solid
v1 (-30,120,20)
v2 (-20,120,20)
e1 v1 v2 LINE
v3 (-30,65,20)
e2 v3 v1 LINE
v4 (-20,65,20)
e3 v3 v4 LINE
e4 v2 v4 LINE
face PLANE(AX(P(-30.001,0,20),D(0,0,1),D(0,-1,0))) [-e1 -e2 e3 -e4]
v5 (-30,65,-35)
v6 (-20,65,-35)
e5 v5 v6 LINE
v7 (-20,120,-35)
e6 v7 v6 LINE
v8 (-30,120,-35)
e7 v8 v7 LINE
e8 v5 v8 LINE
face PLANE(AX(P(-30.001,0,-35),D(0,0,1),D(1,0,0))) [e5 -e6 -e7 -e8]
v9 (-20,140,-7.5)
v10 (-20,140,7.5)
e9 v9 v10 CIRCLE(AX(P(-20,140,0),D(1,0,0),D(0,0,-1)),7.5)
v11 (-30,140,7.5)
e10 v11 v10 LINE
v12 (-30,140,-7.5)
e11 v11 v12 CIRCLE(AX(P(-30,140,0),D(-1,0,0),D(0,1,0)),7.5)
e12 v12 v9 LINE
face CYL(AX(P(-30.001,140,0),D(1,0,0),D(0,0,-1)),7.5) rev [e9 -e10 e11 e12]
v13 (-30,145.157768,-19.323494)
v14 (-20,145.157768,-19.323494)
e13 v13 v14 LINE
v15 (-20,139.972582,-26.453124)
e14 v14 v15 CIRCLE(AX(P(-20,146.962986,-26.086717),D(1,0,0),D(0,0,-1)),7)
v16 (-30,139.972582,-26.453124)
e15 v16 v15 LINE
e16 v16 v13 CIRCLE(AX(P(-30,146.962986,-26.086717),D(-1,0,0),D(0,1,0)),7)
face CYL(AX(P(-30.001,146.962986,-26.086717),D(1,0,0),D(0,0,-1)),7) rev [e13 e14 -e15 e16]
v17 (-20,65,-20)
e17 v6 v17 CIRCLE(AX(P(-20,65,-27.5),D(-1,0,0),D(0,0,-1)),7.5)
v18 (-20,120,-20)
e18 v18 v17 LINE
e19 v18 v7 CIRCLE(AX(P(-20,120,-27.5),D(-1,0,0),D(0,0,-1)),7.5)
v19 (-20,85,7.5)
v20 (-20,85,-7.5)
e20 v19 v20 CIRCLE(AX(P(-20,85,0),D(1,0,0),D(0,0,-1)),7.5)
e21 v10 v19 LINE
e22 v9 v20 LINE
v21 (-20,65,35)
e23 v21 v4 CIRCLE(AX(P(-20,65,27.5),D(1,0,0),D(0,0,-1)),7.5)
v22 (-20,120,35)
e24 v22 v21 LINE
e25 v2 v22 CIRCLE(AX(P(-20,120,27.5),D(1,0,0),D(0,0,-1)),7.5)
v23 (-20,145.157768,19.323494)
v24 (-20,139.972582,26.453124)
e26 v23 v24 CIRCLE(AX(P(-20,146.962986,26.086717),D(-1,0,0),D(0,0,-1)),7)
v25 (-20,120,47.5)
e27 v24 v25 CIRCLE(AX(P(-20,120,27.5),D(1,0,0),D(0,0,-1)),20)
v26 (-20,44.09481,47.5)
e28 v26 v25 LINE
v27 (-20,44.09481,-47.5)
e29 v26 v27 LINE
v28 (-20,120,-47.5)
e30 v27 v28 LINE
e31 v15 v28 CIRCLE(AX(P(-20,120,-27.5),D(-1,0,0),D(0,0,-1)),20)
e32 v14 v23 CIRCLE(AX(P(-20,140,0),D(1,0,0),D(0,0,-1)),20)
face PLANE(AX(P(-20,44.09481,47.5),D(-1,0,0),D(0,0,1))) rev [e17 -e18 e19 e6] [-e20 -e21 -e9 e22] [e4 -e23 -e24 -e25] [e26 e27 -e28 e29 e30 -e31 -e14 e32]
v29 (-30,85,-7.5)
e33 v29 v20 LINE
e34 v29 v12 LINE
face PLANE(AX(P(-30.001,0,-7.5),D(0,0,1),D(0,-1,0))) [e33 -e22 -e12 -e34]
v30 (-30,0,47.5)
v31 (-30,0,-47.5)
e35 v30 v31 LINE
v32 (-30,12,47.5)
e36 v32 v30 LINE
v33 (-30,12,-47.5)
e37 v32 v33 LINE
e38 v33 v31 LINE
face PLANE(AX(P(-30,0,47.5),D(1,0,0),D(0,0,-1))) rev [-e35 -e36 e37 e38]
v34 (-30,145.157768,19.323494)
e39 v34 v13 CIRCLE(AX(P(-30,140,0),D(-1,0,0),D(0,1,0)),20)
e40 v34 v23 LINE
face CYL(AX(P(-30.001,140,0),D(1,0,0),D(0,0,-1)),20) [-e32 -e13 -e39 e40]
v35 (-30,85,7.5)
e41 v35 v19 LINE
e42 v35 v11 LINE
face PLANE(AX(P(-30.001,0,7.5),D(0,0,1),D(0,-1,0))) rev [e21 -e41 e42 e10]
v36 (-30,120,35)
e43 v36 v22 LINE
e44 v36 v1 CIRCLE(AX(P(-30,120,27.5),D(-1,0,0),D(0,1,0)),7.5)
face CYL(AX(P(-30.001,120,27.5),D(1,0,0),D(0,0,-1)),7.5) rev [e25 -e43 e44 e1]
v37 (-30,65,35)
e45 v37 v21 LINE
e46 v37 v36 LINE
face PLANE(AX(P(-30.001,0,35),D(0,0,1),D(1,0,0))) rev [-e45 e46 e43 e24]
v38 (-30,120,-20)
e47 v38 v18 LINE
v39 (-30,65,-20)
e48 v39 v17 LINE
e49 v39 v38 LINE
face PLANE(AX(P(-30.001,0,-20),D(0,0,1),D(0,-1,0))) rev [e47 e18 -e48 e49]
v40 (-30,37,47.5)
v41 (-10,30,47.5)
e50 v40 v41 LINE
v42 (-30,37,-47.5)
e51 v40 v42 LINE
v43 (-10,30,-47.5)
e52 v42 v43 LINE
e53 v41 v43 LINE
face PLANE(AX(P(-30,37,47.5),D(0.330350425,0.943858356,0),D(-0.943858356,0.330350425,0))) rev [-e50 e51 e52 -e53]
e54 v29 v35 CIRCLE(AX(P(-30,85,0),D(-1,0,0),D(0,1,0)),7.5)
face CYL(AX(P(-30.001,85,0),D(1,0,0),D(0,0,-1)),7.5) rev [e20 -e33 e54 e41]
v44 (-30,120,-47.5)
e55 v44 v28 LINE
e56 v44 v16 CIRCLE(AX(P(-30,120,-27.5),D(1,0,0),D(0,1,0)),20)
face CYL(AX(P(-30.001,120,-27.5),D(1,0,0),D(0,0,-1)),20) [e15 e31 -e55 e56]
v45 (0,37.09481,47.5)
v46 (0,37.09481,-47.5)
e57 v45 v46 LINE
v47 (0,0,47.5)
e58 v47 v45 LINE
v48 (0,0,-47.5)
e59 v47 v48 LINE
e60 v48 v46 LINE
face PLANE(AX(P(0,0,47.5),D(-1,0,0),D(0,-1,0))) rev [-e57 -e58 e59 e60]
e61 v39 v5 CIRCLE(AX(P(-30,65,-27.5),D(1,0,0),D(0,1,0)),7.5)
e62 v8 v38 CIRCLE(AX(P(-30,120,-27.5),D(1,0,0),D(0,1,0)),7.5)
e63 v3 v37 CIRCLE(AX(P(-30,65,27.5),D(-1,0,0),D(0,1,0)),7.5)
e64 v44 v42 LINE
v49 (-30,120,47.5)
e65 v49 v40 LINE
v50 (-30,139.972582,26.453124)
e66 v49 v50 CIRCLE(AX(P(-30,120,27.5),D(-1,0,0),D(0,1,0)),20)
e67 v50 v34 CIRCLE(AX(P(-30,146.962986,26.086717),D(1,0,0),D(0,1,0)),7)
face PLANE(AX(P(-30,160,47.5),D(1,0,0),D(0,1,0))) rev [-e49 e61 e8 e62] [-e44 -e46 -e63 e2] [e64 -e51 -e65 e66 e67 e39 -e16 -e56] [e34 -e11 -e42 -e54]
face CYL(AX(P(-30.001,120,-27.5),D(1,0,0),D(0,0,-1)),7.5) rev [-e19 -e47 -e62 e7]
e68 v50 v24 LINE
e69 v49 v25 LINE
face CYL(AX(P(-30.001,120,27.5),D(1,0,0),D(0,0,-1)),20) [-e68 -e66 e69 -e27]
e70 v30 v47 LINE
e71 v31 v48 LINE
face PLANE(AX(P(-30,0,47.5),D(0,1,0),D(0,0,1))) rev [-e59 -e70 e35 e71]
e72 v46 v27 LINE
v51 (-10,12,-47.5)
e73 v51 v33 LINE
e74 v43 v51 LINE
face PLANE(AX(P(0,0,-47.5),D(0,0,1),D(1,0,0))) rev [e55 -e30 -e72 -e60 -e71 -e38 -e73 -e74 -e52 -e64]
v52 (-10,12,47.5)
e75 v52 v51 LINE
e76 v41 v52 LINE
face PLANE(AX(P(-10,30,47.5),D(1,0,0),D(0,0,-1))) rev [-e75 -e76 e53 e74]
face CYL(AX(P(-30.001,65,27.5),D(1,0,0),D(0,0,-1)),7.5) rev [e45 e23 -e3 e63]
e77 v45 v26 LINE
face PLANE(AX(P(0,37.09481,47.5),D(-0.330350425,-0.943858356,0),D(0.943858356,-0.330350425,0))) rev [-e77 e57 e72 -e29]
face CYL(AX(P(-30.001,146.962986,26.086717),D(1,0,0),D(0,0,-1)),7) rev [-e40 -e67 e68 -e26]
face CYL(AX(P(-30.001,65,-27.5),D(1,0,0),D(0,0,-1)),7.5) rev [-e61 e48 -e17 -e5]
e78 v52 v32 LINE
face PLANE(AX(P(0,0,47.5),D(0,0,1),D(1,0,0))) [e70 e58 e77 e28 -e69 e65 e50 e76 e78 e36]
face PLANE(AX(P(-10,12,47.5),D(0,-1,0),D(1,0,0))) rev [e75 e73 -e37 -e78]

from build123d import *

# Parameters (mm, degrees)
SUPPORT_BODY_DEPTH         = 47.5
MOUNTING_SLOTS_3X7MM_REACH = 170.096


with BuildPart() as part:
    # Support Profile Sketch → Support Body (new, symmetric)
    with BuildSketch(Plane.XY):
        Polygon((-30, 0), (0, 0), (0, 37.09481005), (-20, 44.09481005), (-20, 160), (-30, 160), (-30, 37), (-10, 30), (-10, 12), (-30, 12), align=None)
    extrude(amount=SUPPORT_BODY_DEPTH, both=True)

    # Mounting Slots Sketch → Mounting Slots 3x7mm (cut, up to next)
    with BuildSketch(Plane(origin=(-20, 0, 0), x_dir=(0, 0, -1), z_dir=(1, 0, 0)), mode=Mode.PRIVATE) as mounting_slots_3x7mm_sk1:
        with BuildLine():
            Line((-35, 120), (-35, 65))
            ThreePointArc((-35, 65), (-27.5, 57.5), (-20, 65))
            Line((-20, 65), (-20, 120))
            ThreePointArc((-20, 120), (-27.5, 127.5), (-35, 120))
        make_face()
    mounting_slots_3x7mm_tool1 = extrude(mounting_slots_3x7mm_sk1.sketch, amount=-MOUNTING_SLOTS_3X7MM_REACH, mode=Mode.PRIVATE) & part.part
    # Mounting Slots Sketch → Mounting Slots 3x7mm (cut, up to next)
    with BuildSketch(Plane(origin=(-20, 0, 0), x_dir=(0, 0, -1), z_dir=(1, 0, 0)), mode=Mode.PRIVATE) as mounting_slots_3x7mm_sk2:
        with BuildLine():
            Line((-7.5, 140), (-7.5, 85))
            ThreePointArc((-7.5, 85), (0, 77.5), (7.5, 85))
            Line((7.5, 85), (7.5, 140))
            ThreePointArc((7.5, 140), (0, 147.5), (-7.5, 140))
        make_face()
    mounting_slots_3x7mm_tool2 = extrude(mounting_slots_3x7mm_sk2.sketch, amount=-MOUNTING_SLOTS_3X7MM_REACH, mode=Mode.PRIVATE) & part.part
    # Mounting Slots Sketch → Mounting Slots 3x7mm (cut, up to next)
    with BuildSketch(Plane(origin=(-20, 0, 0), x_dir=(0, 0, -1), z_dir=(1, 0, 0)), mode=Mode.PRIVATE) as mounting_slots_3x7mm_sk3:
        with BuildLine():
            ThreePointArc((35, 65), (27.5, 57.5), (20, 65))
            Line((20, 65), (20, 120))
            ThreePointArc((20, 120), (27.5, 127.5), (35, 120))
            Line((35, 120), (35, 65))
        make_face()
    mounting_slots_3x7mm_tool3 = extrude(mounting_slots_3x7mm_sk3.sketch, amount=-MOUNTING_SLOTS_3X7MM_REACH, mode=Mode.PRIVATE) & part.part
    # Mounting Slots Sketch → Mounting Slots 3x7mm (cut, up to next)
    with BuildSketch(Plane(origin=(-20, 0, 0), x_dir=(0, 0, -1), z_dir=(1, 0, 0)), mode=Mode.PRIVATE) as mounting_slots_3x7mm_sk4:
        with BuildLine():
            ThreePointArc((26.453123952, 139.97258247), (41.267034521, 134.507541504), (47.5, 120))
            Line((47.5, 120), (47.5, 160))
            Line((47.5, 160), (1.13e-07, 160))
            ThreePointArc((1.13e-07, 160), (12.182870127, 155.861200316), (19.323494322, 145.157767656))
            ThreePointArc((19.323494322, 145.157767656), (21.969515451, 141.301833745), (26.453123952, 139.97258247))
        make_face()
    mounting_slots_3x7mm_tool4 = extrude(mounting_slots_3x7mm_sk4.sketch, amount=-MOUNTING_SLOTS_3X7MM_REACH, mode=Mode.PRIVATE) & part.part
    # Mounting Slots Sketch → Mounting Slots 3x7mm (cut, up to next)
    with BuildSketch(Plane(origin=(-20, 0, 0), x_dir=(0, 0, -1), z_dir=(1, 0, 0)), mode=Mode.PRIVATE) as mounting_slots_3x7mm_sk5:
        with BuildLine():
            ThreePointArc((-19.323494322, 145.157767656), (-12.182870037, 155.861200385), (1.13e-07, 160))
            Line((1.13e-07, 160), (-47.5, 160))
            Line((-47.5, 160), (-47.5, 120))
            ThreePointArc((-47.5, 120), (-41.267034521, 134.507541504), (-26.453123952, 139.97258247))
            ThreePointArc((-26.453123952, 139.97258247), (-21.969515451, 141.301833745), (-19.323494322, 145.157767656))
        make_face()
    mounting_slots_3x7mm_tool5 = extrude(mounting_slots_3x7mm_sk5.sketch, amount=-MOUNTING_SLOTS_3X7MM_REACH, mode=Mode.PRIVATE) & part.part
    add(mounting_slots_3x7mm_tool1.solids().sort_by_distance((-20, 92.5, 27.5))[0], mode=Mode.SUBTRACT)
    add(mounting_slots_3x7mm_tool2.solids().sort_by_distance((-20, 112.5, 0))[0], mode=Mode.SUBTRACT)
    add(mounting_slots_3x7mm_tool3.solids().sort_by_distance((-20, 92.5, -27.5))[0], mode=Mode.SUBTRACT)
    add(mounting_slots_3x7mm_tool4.solids().sort_by_distance((-20, 149.008344, -32.791963))[0], mode=Mode.SUBTRACT)
    add(mounting_slots_3x7mm_tool5.solids().sort_by_distance((-20, 149.008344, 32.791963))[0], mode=Mode.SUBTRACT)


solid = part.part
